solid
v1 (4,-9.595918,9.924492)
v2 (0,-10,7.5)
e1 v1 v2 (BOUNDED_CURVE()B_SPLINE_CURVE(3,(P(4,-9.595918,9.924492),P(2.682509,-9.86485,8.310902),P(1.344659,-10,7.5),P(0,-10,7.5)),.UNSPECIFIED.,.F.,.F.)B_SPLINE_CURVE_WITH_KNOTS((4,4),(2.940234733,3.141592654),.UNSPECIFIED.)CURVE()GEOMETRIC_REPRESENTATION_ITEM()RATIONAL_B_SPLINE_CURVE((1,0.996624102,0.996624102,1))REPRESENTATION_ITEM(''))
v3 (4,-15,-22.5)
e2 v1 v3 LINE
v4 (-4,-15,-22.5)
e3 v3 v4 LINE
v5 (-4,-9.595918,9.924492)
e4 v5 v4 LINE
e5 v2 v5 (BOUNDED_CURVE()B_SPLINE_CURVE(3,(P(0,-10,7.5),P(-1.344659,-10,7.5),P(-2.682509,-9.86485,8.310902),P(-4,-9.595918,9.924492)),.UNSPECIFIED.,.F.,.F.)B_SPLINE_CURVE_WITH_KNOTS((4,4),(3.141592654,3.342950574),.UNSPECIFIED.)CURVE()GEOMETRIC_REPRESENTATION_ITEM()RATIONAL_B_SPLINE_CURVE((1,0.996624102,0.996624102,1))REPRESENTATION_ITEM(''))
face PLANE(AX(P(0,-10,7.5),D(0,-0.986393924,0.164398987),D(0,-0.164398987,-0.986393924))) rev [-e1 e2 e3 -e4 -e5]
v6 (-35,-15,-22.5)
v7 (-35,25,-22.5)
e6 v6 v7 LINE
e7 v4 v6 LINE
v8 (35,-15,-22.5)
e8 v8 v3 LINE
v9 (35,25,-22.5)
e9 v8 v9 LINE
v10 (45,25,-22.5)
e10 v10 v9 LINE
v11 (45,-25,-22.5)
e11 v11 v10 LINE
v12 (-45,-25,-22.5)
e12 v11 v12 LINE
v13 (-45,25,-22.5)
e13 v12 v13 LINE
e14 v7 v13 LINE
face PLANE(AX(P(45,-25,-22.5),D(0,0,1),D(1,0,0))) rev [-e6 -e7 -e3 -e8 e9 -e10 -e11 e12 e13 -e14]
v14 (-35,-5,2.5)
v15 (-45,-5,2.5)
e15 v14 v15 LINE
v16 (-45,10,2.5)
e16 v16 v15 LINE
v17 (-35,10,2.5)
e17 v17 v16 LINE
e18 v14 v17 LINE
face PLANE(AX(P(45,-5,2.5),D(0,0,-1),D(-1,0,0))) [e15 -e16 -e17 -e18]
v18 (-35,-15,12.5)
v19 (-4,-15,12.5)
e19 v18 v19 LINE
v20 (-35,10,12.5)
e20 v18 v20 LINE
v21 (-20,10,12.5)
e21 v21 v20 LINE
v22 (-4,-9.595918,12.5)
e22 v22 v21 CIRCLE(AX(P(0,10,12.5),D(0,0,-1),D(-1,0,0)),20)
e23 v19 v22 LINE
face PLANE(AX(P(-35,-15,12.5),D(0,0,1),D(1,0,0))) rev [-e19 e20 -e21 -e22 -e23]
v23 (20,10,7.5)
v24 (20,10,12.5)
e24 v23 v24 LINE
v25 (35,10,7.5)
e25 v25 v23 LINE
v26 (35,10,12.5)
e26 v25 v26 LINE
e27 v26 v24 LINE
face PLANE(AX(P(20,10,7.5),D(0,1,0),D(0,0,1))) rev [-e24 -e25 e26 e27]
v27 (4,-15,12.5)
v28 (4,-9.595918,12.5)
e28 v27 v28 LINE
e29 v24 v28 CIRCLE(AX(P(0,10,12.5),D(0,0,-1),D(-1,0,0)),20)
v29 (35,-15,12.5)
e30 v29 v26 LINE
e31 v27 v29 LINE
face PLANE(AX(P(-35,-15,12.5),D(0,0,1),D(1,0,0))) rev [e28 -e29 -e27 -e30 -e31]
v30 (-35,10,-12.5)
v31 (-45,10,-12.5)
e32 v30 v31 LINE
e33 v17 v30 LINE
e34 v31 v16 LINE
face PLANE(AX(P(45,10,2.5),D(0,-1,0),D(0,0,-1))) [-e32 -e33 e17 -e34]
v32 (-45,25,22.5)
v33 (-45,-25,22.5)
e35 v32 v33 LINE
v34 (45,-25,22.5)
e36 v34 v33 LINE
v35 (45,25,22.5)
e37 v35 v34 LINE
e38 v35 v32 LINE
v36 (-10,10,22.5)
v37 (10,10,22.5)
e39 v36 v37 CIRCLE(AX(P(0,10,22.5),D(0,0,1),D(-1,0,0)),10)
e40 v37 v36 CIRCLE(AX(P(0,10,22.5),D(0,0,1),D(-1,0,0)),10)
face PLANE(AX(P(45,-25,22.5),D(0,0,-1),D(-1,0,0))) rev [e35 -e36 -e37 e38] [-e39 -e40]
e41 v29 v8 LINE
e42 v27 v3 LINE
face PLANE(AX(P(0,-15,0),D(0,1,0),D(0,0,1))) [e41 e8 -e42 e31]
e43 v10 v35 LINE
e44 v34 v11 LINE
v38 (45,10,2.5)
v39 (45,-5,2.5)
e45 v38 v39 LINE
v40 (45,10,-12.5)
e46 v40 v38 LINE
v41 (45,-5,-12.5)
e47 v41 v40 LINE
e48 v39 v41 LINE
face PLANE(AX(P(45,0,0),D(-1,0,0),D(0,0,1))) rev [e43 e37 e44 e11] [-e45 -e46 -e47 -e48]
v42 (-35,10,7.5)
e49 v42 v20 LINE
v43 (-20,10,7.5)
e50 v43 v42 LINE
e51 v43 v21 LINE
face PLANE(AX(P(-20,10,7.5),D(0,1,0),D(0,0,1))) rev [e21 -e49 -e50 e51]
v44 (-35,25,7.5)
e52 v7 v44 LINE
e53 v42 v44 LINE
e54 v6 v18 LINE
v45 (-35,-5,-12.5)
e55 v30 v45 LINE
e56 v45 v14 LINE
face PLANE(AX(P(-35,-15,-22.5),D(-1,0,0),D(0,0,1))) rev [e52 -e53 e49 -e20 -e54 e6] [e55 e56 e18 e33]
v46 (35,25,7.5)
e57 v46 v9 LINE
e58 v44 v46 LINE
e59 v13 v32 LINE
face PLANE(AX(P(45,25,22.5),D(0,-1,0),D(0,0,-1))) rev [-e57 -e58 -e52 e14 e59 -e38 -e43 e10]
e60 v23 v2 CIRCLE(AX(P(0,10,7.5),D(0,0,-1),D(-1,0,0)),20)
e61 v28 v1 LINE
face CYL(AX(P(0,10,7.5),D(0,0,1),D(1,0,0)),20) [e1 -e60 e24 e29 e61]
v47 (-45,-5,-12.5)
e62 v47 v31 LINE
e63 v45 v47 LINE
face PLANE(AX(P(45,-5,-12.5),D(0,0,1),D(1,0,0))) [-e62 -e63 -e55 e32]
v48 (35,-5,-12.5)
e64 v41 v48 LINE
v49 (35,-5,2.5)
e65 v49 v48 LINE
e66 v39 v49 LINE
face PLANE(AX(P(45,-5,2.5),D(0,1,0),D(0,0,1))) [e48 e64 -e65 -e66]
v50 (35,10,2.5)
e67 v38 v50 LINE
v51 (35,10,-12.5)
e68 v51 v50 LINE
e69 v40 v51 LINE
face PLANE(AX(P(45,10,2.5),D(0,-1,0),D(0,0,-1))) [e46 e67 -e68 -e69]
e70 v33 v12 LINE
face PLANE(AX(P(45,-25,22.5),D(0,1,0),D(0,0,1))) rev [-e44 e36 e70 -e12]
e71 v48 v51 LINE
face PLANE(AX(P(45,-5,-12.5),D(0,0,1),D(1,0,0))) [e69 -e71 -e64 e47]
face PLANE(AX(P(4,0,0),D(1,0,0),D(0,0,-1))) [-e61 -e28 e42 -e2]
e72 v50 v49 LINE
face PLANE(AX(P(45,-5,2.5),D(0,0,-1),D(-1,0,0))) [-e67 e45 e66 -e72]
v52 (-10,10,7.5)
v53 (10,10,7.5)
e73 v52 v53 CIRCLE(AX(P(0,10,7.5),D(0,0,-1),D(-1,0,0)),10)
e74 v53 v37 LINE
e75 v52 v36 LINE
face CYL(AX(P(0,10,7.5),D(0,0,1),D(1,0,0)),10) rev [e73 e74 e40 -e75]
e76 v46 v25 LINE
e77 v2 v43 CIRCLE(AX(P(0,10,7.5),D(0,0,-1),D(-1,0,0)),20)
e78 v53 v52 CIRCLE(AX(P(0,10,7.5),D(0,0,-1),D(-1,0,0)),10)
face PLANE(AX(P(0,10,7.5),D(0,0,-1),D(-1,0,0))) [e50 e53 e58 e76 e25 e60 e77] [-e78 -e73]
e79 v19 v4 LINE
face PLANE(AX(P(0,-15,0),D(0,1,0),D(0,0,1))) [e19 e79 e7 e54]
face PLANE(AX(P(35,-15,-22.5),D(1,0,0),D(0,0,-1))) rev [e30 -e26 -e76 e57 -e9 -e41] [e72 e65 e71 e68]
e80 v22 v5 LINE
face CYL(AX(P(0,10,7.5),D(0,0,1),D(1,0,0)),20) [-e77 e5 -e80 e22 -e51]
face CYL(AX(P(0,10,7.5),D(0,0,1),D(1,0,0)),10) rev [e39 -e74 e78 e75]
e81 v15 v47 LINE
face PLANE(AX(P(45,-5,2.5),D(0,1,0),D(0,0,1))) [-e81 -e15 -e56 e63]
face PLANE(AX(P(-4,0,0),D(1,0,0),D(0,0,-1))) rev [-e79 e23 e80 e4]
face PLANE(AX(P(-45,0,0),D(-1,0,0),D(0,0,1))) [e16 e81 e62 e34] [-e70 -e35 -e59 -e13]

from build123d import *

# Parameters (mm, degrees)
BLOCK_PROFILE_SKETCH_W    = 45
BLOCK_PROFILE_SKETCH_H    = 50
BLOCK_PROFILE_SKETCH_W_2  = 15
BLOCK_PROFILE_SKETCH_H_2  = 15
BLOCK_BODY_90MM_DEPTH     = 45
CENTER_POCKET_SKETCH_W    = 70
CENTER_POCKET_SKETCH_H    = 35
CENTER_POCKET_35X70_DEPTH = 40
POCKET_PAD_SKETCH_R       = 10
POCKET_PAD_5MM_DEPTH      = 5
SIDE_HOLE_REACH           = 64.249
SIDE_HOLE_SKETCH_R        = 10
SUPPORT_RIB_8MM_REACH     = 58.181
SUPPORT_RIB_SKETCH_WALL_W = 144.774837922
SUPPORT_RIB_SKETCH_WALL_H = 8


with BuildPart() as part:
    # Block Profile Sketch → Block Body 90mm (new, symmetric)
    with BuildSketch(Plane(origin=(0, 0, 0), x_dir=(0, 0, -1), z_dir=(1, 0, 0))):
        Rectangle(BLOCK_PROFILE_SKETCH_W, BLOCK_PROFILE_SKETCH_H)
        with Locations((5, 2.5)):
            Rectangle(BLOCK_PROFILE_SKETCH_W_2, BLOCK_PROFILE_SKETCH_H_2, mode=Mode.SUBTRACT)
    extrude(amount=BLOCK_BODY_90MM_DEPTH, both=True)

    # Center Pocket Sketch → Center Pocket 35x70 (cut)
    with BuildSketch(Plane(origin=(0, 25, 0), x_dir=(1, 0, 0), z_dir=(0, 1, 0))):
        with Locations((0, 5)):
            Rectangle(CENTER_POCKET_SKETCH_W, CENTER_POCKET_SKETCH_H)
    extrude(amount=-CENTER_POCKET_35X70_DEPTH, mode=Mode.SUBTRACT)

    # Pocket Pad Sketch → Pocket Pad 5mm (add)
    with BuildSketch(Plane(origin=(0, 0, 12.5), x_dir=(-1, 0, 0), z_dir=(0, 0, -1))):
        with BuildLine():
            Line((20, 10), (35, 10))
            Line((35, 10), (35, 25))
            Line((35, 25), (-35, 25))
            Line((-35, 25), (-35, 10))
            Line((-35, 10), (-20, 10))
            ThreePointArc((-20, 10), (0, -10), (20, 10))
        make_face()
        with Locations((0, 10)):
            Circle(POCKET_PAD_SKETCH_R, mode=Mode.SUBTRACT)
    extrude(amount=POCKET_PAD_5MM_DEPTH)

    # Side Hole Sketch → Side Hole (cut, up to next)
    with BuildSketch(Plane(origin=(0, 0, 12.5), x_dir=(-1, 0, 0), z_dir=(0, 0, -1)), mode=Mode.PRIVATE) as side_hole_sk1:
        with Locations((0, 10)):
            Circle(SIDE_HOLE_SKETCH_R)
    side_hole_tool1 = extrude(side_hole_sk1.sketch, amount=-SIDE_HOLE_REACH, mode=Mode.PRIVATE) & part.part
    add(side_hole_tool1.solids().sort_by_distance((0, 10, 12.5))[0], mode=Mode.SUBTRACT)

    # Support Rib Sketch wall → Support Rib 8mm (add, up to next)
    with BuildSketch(Plane(origin=(0, -12.5, -7.5), x_dir=(0, -0.164398987305, -0.986393923832), z_dir=(0, 0.986393923832, -0.164398987305)), mode=Mode.PRIVATE) as support_rib_8mm_sk1:
        Rectangle(SUPPORT_RIB_SKETCH_WALL_W, SUPPORT_RIB_SKETCH_WALL_H)
    support_rib_8mm_tool1 = extrude(support_rib_8mm_sk1.sketch, amount=-SUPPORT_RIB_8MM_REACH, mode=Mode.PRIVATE) - part.part
    add(support_rib_8mm_tool1.solids().sort_by_distance((0, -12.5, -7.5))[0])


solid = part.part
